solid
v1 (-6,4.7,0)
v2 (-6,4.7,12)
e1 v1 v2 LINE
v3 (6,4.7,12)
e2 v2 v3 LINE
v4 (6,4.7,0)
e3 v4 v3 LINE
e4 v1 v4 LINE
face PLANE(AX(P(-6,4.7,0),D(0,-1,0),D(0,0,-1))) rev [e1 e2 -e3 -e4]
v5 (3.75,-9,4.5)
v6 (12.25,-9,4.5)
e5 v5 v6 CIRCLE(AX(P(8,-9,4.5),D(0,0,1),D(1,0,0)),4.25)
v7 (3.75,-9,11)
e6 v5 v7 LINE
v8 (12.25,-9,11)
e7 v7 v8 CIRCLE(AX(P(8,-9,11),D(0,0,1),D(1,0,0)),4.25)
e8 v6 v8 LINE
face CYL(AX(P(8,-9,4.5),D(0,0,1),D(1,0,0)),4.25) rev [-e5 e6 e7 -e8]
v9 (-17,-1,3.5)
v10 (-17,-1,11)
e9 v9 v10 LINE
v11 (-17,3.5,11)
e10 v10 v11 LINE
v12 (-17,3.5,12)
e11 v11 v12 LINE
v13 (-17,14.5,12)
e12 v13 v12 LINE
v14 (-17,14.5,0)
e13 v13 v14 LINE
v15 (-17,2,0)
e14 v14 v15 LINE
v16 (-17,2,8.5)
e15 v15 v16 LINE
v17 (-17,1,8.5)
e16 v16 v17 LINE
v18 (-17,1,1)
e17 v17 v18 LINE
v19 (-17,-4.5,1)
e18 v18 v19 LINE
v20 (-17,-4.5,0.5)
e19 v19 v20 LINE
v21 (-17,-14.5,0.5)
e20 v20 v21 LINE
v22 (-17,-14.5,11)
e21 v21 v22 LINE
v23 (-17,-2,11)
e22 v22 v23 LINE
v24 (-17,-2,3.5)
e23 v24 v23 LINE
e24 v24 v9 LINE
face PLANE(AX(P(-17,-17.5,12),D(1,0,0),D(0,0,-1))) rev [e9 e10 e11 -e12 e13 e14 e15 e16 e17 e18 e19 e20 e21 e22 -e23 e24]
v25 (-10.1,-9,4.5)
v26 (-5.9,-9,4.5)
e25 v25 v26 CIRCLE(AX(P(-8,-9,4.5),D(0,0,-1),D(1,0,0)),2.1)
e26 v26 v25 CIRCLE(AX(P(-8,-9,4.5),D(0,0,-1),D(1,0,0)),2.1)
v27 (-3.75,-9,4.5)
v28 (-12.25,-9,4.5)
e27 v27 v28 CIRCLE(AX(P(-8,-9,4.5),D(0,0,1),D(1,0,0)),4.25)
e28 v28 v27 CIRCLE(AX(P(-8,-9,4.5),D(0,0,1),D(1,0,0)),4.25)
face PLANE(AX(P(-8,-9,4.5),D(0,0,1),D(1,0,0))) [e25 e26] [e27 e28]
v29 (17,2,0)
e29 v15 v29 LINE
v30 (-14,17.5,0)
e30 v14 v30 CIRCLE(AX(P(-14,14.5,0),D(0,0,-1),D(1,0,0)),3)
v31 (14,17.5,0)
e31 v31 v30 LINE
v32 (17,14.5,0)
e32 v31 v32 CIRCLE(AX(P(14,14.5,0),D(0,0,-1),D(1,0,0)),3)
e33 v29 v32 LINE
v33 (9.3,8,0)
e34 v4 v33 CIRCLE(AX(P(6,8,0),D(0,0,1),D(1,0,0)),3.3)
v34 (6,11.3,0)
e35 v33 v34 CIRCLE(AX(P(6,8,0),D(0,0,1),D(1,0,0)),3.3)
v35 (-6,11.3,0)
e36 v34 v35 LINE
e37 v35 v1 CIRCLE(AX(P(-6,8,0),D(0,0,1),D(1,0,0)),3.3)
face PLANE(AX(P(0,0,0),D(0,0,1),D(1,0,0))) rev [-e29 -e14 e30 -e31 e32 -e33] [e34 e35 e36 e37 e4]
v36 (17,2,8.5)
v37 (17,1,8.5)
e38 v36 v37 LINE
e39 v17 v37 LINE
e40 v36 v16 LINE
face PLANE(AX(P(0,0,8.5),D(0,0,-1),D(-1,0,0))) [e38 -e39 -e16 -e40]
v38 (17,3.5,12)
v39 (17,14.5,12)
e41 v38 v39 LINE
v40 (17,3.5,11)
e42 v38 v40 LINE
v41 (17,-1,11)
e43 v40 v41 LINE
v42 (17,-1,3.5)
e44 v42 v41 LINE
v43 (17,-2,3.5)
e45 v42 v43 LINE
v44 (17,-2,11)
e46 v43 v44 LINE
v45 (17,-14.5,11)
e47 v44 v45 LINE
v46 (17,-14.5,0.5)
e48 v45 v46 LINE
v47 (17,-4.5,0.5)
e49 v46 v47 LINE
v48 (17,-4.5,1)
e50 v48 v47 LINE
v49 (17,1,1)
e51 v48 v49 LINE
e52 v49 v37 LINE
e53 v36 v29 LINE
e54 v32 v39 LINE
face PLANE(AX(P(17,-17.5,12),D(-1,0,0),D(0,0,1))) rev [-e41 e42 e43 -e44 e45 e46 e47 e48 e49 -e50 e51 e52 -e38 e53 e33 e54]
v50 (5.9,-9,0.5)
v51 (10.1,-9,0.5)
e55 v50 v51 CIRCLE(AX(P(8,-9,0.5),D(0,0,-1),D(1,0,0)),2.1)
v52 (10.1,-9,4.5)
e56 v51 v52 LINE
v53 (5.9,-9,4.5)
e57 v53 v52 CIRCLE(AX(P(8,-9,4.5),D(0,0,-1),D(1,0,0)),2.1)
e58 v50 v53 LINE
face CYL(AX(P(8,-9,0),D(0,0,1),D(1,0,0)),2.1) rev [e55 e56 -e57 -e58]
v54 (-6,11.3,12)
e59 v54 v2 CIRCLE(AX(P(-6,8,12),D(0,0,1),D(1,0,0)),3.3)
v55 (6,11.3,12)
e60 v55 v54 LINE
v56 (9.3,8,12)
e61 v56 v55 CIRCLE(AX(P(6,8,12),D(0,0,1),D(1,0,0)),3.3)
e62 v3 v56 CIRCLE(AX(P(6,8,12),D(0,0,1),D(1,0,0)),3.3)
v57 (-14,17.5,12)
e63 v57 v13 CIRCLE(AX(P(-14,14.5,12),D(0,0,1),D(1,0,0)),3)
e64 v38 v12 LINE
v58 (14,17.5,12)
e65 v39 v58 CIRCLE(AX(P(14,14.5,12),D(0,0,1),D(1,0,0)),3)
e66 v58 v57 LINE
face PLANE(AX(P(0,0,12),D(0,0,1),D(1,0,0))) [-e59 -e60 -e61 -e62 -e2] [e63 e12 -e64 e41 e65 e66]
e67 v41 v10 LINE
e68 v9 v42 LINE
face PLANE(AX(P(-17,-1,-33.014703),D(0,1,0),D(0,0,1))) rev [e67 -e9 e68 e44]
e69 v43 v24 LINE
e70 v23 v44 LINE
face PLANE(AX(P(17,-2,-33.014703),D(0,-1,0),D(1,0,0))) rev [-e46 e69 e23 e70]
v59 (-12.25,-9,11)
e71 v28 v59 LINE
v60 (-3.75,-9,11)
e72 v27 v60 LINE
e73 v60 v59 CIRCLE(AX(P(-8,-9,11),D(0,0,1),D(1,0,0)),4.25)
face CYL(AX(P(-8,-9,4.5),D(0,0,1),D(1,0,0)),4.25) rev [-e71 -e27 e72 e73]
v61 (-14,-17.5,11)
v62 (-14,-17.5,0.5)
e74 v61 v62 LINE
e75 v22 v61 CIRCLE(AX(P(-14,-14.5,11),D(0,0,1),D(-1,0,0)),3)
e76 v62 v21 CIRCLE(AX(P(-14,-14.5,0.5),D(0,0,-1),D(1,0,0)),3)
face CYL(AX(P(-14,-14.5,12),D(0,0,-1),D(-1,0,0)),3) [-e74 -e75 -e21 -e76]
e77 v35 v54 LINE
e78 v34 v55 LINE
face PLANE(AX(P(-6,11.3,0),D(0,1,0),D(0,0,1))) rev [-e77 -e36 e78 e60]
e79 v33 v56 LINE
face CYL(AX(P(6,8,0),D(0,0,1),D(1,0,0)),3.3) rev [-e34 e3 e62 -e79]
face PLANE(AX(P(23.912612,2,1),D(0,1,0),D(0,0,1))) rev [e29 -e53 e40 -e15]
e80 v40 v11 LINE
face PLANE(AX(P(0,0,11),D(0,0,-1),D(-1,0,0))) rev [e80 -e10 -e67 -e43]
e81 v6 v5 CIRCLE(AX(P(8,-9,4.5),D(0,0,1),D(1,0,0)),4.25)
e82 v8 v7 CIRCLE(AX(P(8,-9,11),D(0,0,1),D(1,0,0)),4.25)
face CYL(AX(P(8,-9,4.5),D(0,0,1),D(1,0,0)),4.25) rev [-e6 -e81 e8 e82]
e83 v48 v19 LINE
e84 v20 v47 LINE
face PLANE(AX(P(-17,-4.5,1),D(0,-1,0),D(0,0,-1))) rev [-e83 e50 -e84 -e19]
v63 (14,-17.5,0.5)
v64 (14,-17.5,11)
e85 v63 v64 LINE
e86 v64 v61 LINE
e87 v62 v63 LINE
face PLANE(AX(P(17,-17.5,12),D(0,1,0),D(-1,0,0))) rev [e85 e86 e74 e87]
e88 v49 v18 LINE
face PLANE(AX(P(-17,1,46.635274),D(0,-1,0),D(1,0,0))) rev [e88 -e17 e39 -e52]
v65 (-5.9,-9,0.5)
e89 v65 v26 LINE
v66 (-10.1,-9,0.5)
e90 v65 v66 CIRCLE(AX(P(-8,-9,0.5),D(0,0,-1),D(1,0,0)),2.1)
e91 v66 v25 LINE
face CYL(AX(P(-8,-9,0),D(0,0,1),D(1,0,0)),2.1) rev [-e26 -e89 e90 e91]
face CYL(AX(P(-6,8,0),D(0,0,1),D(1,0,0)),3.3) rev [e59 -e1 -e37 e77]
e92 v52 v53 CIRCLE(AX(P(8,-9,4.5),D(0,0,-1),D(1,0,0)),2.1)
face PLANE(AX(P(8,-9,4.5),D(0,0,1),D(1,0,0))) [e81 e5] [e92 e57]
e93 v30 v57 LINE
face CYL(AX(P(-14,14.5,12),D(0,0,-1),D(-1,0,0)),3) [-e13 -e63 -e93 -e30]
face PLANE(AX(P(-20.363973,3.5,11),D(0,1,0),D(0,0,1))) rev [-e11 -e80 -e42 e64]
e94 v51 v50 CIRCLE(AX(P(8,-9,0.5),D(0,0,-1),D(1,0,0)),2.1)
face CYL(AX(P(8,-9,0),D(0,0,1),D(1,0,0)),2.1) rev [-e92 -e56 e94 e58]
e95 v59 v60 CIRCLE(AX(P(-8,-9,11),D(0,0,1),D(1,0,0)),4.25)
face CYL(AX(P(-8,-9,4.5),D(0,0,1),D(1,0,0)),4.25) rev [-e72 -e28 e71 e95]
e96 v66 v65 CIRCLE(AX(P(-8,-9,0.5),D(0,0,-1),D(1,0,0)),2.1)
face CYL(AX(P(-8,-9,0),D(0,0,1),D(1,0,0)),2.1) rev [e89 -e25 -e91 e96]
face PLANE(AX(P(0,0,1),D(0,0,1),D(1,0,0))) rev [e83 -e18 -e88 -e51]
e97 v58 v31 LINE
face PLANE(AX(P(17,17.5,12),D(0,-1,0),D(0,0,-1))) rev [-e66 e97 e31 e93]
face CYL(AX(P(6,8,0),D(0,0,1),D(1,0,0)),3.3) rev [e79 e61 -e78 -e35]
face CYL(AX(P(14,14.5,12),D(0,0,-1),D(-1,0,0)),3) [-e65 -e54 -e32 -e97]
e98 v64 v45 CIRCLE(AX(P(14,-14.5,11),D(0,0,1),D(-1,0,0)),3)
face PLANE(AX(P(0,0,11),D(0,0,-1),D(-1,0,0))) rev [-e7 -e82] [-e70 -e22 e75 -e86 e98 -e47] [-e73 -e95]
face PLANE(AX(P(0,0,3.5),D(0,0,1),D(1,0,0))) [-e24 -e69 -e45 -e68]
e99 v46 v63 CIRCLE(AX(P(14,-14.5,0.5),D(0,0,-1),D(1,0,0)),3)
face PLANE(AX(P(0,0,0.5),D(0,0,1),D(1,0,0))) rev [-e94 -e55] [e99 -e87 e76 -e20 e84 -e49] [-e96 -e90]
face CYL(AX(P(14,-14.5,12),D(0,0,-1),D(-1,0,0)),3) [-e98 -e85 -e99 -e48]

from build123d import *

# Parameters (mm, degrees)
SKETCH1_W           = 34
SKETCH1_H           = 35
BOSS_EXTRUDE1_DEPTH = 12
SKETCH2_R           = 2.1
CUT_EXTRUDE1_DEPTH  = 28.189152249
SKETCH3_W           = 43.383687714
SKETCH3_H           = 21.18675689
CUT_EXTRUDE2_DEPTH  = 1
SKETCH4_W           = 50.621361837
SKETCH4_H           = 17.880513978
CUT_EXTRUDE3_DEPTH  = 0.5
CUT_EXTRUDE4_DEPTH  = 1
SKETCH6_R           = 4.25
CUT_EXTRUDE5_DEPTH  = 6.5
SKETCH7_W           = 35.621240015
SKETCH7_H           = 1
CUT_EXTRUDE6_DEPTH  = 7.5
SKETCH8_W           = 34
SKETCH8_H           = 1
CUT_EXTRUDE7_DEPTH  = 7.5
FILLET1_R           = 3


with BuildPart() as part:
    # Sketch1 → Boss-Extrude1 (new body)
    with BuildSketch(Plane.XY):
        Rectangle(SKETCH1_W, SKETCH1_H)
    extrude(amount=BOSS_EXTRUDE1_DEPTH)

    # Sketch2 → Cut-Extrude1 (cut, through all)
    with BuildSketch(Plane.XY.offset(12)):
        with Locations((-8, -9)):
            Circle(SKETCH2_R)
        with Locations((8, -9)):
            Circle(SKETCH2_R)
        with BuildLine():
            Line((-6, 11.3), (6, 11.3))
            ThreePointArc((6, 11.3), (9.3, 8), (6, 4.7))
            Line((6, 4.7), (-6, 4.7))
            ThreePointArc((-6, 4.7), (-9.3, 8), (-6, 11.3))
        make_face()
    extrude(amount=-CUT_EXTRUDE1_DEPTH, mode=Mode.SUBTRACT)

    # Sketch3 → Cut-Extrude2 (cut)
    with BuildSketch(Plane.XY.offset(12)):
        with Locations((1.327871271, -7.093378445)):
            Rectangle(SKETCH3_W, SKETCH3_H)
    extrude(amount=-CUT_EXTRUDE2_DEPTH, mode=Mode.SUBTRACT)

    # Sketch4 → Cut-Extrude3 (cut)
    with BuildSketch(Plane(origin=(0, 0, 0), x_dir=(-1, 0, 0), z_dir=(0, 0, -1))):
        with Locations((0.547748923, -13.440256989)):
            Rectangle(SKETCH4_W, SKETCH4_H)
    extrude(amount=-CUT_EXTRUDE3_DEPTH, mode=Mode.SUBTRACT)

    # Sketch5 → Cut-Extrude4 (cut)
    with BuildSketch(Plane(origin=(0, 0, 0), x_dir=(-1, 0, 0), z_dir=(0, 0, -1))):
        Polygon((-23.912611607, 2), (26.337975431, 2), (17, -4.5), (-17, -4.5), align=None)
    extrude(amount=-CUT_EXTRUDE4_DEPTH, mode=Mode.SUBTRACT)

    # Sketch6 → Cut-Extrude5 (cut)
    with BuildSketch(Plane.XY.offset(11)):
        with Locations((8, -9)):
            Circle(SKETCH6_R)
        with Locations((-8, -9)):
            Circle(SKETCH6_R)
    extrude(amount=-CUT_EXTRUDE5_DEPTH, mode=Mode.SUBTRACT)

    # Sketch7 → Cut-Extrude6 (cut)
    with BuildSketch(Plane(origin=(0, 0, 1), x_dir=(-1, 0, 0), z_dir=(0, 0, -1))):
        with Locations((-0.810620008, 1.5)):
            Rectangle(SKETCH7_W, SKETCH7_H)
    extrude(amount=-CUT_EXTRUDE6_DEPTH, mode=Mode.SUBTRACT)

    # Sketch8 → Cut-Extrude7 (cut)
    with BuildSketch(Plane.XY.offset(11)):
        with Locations((0, -1.5)):
            Rectangle(SKETCH8_W, SKETCH8_H)
    extrude(amount=-CUT_EXTRUDE7_DEPTH, mode=Mode.SUBTRACT)

    # Fillet1
    fillet1_edges = [part.edges().sort_by_distance(p)[0] for p in [
        (17, -17.5, 5.75),
        (-17, -17.5, 5.75),
        (-17, 17.5, 6),
        (17, 17.5, 6),
    ]]
    fillet(fillet1_edges, radius=FILLET1_R)


solid = part.part
